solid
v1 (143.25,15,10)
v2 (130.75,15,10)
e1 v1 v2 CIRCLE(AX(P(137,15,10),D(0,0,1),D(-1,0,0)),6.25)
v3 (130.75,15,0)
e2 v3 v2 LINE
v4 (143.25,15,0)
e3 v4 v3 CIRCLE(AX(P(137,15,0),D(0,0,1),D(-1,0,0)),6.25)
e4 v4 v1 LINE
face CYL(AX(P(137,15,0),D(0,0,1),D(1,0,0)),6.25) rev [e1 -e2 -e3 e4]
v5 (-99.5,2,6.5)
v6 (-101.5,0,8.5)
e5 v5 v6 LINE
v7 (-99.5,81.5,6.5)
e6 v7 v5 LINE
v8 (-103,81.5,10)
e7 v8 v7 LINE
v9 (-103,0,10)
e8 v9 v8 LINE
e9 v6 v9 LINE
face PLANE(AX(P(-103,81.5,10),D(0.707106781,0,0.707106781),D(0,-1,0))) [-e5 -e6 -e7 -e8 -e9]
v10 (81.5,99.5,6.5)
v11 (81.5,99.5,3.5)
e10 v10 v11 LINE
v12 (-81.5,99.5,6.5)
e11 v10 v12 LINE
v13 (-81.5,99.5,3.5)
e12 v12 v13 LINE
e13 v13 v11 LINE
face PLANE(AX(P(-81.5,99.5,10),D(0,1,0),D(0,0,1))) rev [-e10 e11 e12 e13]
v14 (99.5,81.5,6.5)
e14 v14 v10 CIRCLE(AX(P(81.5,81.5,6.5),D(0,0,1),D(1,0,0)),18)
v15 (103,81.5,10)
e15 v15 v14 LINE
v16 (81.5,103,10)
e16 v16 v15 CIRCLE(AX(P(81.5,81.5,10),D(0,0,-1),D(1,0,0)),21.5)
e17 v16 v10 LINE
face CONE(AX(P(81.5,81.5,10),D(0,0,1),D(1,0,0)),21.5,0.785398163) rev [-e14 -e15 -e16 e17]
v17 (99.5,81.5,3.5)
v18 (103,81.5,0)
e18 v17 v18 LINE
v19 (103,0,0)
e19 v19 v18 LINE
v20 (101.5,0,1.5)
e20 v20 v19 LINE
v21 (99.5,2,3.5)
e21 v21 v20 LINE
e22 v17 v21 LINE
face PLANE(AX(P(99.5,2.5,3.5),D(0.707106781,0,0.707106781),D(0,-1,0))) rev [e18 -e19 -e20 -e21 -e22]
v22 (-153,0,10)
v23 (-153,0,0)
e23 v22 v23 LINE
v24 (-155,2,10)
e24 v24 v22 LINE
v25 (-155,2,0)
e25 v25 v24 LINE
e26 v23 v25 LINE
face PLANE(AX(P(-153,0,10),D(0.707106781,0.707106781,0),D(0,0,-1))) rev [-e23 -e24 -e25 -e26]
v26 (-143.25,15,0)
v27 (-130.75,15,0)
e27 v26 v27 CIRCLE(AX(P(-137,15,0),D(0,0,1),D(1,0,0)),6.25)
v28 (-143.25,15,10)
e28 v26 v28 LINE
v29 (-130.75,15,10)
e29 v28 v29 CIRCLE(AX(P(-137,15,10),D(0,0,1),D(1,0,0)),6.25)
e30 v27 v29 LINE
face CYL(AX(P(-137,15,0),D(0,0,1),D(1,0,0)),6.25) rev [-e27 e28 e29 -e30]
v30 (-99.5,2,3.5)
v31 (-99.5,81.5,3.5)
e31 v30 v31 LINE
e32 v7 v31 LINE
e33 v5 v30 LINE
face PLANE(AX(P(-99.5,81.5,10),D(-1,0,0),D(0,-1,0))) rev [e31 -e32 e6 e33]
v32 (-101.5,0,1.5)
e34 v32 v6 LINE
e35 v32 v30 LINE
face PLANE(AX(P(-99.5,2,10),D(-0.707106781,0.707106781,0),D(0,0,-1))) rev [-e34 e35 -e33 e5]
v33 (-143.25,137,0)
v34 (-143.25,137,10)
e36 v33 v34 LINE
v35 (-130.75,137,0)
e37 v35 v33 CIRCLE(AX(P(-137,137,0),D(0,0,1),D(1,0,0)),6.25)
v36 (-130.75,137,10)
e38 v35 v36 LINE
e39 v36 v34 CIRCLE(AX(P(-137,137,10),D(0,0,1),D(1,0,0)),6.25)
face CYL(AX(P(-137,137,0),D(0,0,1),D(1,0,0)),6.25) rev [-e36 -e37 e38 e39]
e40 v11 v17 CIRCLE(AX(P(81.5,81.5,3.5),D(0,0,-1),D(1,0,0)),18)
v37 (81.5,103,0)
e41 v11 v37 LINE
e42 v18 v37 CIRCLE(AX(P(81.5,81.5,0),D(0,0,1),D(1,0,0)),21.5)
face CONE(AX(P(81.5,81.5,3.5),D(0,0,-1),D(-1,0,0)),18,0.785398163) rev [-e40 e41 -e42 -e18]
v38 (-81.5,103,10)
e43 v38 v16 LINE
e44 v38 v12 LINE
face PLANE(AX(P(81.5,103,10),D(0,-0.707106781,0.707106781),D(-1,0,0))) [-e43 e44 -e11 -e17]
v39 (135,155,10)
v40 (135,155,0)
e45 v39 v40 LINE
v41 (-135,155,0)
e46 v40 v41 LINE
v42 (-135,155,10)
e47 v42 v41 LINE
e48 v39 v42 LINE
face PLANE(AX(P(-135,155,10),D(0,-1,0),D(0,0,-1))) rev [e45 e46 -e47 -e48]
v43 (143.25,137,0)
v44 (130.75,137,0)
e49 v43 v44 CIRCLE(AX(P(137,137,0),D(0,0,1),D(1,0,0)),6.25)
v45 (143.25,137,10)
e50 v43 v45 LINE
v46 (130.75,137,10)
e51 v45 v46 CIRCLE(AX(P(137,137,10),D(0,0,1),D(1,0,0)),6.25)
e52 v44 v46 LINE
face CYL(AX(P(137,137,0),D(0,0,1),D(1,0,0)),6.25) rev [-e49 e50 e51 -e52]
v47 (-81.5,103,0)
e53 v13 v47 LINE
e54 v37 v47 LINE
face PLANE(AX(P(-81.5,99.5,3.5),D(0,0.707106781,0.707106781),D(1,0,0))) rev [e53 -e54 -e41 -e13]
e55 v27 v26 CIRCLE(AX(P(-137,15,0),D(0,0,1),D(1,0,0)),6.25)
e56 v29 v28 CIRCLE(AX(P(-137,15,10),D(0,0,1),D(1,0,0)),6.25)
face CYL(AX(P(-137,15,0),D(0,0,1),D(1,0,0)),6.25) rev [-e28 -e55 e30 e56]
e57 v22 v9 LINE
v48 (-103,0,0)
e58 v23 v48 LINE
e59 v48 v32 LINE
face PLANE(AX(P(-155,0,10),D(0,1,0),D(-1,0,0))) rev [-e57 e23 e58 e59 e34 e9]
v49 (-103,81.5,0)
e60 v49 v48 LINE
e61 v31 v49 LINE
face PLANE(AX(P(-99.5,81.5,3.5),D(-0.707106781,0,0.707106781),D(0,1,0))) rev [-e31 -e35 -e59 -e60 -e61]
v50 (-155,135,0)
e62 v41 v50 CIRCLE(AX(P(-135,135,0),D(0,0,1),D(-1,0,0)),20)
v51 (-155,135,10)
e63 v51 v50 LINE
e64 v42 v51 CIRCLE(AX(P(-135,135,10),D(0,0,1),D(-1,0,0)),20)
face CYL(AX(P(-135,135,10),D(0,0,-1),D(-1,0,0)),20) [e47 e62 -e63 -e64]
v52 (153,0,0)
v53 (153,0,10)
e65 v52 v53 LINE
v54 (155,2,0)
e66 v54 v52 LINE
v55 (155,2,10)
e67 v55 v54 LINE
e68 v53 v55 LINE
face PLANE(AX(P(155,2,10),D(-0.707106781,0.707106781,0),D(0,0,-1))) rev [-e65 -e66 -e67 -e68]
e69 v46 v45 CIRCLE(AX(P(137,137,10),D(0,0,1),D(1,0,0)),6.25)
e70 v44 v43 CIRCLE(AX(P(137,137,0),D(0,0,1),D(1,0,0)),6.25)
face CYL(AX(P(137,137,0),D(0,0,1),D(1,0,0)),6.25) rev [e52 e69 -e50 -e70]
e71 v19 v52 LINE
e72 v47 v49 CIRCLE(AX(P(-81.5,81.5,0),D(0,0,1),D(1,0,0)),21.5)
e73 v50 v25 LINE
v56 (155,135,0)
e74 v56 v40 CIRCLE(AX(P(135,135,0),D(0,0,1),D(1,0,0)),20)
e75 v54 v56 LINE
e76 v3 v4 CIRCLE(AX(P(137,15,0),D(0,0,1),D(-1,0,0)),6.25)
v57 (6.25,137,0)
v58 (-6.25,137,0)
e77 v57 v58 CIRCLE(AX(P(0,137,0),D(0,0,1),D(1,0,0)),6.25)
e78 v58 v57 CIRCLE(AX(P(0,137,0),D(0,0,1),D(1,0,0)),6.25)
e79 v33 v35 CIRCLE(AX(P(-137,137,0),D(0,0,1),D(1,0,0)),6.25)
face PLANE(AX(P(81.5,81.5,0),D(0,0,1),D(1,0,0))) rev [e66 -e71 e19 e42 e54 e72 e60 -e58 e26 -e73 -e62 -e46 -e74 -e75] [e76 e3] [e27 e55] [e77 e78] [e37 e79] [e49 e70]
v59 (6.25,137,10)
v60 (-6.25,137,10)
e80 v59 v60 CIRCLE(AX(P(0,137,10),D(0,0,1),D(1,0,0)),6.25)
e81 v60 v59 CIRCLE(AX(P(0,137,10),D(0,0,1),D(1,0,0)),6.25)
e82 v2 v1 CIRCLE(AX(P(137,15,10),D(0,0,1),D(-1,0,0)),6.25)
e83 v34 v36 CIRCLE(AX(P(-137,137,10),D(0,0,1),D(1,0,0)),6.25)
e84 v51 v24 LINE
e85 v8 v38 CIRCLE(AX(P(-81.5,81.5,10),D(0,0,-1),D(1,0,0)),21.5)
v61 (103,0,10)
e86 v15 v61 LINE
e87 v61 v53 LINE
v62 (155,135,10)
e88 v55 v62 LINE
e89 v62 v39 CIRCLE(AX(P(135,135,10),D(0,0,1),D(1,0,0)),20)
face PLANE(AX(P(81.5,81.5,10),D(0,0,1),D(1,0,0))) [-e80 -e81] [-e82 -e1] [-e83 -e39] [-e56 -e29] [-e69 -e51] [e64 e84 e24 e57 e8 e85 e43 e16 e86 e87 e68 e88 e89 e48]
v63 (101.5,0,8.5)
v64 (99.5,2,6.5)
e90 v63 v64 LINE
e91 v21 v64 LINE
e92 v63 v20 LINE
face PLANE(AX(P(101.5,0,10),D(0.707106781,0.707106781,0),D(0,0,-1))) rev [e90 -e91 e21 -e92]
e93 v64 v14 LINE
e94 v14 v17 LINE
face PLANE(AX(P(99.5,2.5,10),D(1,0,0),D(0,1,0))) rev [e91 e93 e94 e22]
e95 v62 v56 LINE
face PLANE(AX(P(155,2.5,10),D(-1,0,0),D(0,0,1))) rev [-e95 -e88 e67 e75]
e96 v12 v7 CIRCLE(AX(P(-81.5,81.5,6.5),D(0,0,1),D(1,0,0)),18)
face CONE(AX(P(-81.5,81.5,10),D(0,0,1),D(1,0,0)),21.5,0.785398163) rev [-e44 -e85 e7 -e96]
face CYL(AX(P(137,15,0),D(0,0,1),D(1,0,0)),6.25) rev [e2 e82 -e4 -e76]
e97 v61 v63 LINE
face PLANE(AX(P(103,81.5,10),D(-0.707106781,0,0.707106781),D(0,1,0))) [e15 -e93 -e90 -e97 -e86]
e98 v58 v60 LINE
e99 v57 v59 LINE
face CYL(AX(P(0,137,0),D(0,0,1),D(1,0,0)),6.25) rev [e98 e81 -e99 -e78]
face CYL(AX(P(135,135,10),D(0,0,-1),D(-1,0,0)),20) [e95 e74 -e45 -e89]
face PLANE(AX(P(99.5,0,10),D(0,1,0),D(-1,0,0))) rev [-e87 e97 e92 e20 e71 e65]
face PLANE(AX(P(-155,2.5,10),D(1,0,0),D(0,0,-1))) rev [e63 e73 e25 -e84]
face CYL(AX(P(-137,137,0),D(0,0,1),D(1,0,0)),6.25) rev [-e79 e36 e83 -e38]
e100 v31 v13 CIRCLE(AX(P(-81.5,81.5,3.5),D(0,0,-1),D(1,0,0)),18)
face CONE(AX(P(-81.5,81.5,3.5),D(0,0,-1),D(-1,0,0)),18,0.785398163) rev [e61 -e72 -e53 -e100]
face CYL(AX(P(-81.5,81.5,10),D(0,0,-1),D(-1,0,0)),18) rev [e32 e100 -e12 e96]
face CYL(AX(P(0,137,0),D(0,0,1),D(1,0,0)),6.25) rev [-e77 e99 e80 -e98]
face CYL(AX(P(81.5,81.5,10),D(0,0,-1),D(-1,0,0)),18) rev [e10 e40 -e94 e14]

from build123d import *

# Parameters (mm, degrees)
EXTRUDE_1_DEPTH     = 10
SKETCH_2_R          = 6.25
CUT_EXTRUDE_1_DEPTH = 220.431082575
CHAMFER_1_SIZE      = 2
CHAMFER_2_SIZE      = 3.5


with BuildPart() as part:
    # 草图1 → 凸台-拉伸1 (new body)
    with BuildSketch(Plane.XY):
        with BuildLine():
            Line((-155, 0), (-99.5, 0))
            Line((-99.5, 0), (-99.5, 2.5))
            Line((-99.5, 2.5), (-99.5, 81.5))
            ThreePointArc((-99.5, 81.5), (-94.227922061, 94.227922061), (-81.5, 99.5))
            Line((-81.5, 99.5), (81.5, 99.5))
            ThreePointArc((81.5, 99.5), (94.227922061, 94.227922061), (99.5, 81.5))
            Line((99.5, 81.5), (99.5, 2.5))
            Line((99.5, 2.5), (99.5, 0))
            Line((99.5, 0), (155, 0))
            Line((155, 0), (155, 2.5))
            Line((155, 2.5), (155, 135))
            ThreePointArc((155, 135), (149.142135624, 149.142135624), (135, 155))
            Line((135, 155), (-135, 155))
            ThreePointArc((-135, 155), (-149.142135624, 149.142135624), (-155, 135))
            Line((-155, 135), (-155, 2.5))
            Line((-155, 2.5), (-155, 0))
        make_face()
    extrude(amount=EXTRUDE_1_DEPTH)

    # 草图2 → 切除-拉伸1 (cut, through all)
    with BuildSketch(Plane.XY.offset(10)):
        with Locations((0, 137)):
            Circle(SKETCH_2_R)
        with Locations((0, -137)):
            Circle(SKETCH_2_R)
        with Locations((-137, 137)):
            Circle(SKETCH_2_R)
        with Locations((137, 137)):
            Circle(SKETCH_2_R)
        with Locations((-137, -137)):
            Circle(SKETCH_2_R)
        with Locations((137, -137)):
            Circle(SKETCH_2_R)
        with Locations((-137, 15)):
            Circle(SKETCH_2_R)
        with Locations((-137, -15)):
            Circle(SKETCH_2_R)
        with Locations((137, -15)):
            Circle(SKETCH_2_R)
        with Locations(Location((137, 15, 0), (0, 0, 180))):
            Circle(SKETCH_2_R)
    extrude(amount=-CUT_EXTRUDE_1_DEPTH, mode=Mode.SUBTRACT)

    # 倒角1
    chamfer_1_edges = [part.edges().sort_by_distance(p)[0] for p in [
        (-99.5, 0, 5),
        (-155, 0, 5),
        (155, 0, 5),
        (99.5, 0, 5),
    ]]
    chamfer(chamfer_1_edges, length=CHAMFER_1_SIZE)

    # 倒角2
    chamfer_2_edges = [part.edges().sort_by_distance(p)[0] for p in [
        (99.5, 41.75, 0),
        (94.227922061, 94.227922061, 0),
        (0, 99.5, 0),
        (-94.227922061, 94.227922061, 0),
        (-99.5, 41.75, 0),
        (99.5, 41.75, 10),
        (94.227922061, 94.227922061, 10),
        (-99.5, 41.75, 10),
        (-94.227922061, 94.227922061, 10),
        (0, 99.5, 10),
    ]]
    chamfer(chamfer_2_edges, length=CHAMFER_2_SIZE)


solid = part.part
